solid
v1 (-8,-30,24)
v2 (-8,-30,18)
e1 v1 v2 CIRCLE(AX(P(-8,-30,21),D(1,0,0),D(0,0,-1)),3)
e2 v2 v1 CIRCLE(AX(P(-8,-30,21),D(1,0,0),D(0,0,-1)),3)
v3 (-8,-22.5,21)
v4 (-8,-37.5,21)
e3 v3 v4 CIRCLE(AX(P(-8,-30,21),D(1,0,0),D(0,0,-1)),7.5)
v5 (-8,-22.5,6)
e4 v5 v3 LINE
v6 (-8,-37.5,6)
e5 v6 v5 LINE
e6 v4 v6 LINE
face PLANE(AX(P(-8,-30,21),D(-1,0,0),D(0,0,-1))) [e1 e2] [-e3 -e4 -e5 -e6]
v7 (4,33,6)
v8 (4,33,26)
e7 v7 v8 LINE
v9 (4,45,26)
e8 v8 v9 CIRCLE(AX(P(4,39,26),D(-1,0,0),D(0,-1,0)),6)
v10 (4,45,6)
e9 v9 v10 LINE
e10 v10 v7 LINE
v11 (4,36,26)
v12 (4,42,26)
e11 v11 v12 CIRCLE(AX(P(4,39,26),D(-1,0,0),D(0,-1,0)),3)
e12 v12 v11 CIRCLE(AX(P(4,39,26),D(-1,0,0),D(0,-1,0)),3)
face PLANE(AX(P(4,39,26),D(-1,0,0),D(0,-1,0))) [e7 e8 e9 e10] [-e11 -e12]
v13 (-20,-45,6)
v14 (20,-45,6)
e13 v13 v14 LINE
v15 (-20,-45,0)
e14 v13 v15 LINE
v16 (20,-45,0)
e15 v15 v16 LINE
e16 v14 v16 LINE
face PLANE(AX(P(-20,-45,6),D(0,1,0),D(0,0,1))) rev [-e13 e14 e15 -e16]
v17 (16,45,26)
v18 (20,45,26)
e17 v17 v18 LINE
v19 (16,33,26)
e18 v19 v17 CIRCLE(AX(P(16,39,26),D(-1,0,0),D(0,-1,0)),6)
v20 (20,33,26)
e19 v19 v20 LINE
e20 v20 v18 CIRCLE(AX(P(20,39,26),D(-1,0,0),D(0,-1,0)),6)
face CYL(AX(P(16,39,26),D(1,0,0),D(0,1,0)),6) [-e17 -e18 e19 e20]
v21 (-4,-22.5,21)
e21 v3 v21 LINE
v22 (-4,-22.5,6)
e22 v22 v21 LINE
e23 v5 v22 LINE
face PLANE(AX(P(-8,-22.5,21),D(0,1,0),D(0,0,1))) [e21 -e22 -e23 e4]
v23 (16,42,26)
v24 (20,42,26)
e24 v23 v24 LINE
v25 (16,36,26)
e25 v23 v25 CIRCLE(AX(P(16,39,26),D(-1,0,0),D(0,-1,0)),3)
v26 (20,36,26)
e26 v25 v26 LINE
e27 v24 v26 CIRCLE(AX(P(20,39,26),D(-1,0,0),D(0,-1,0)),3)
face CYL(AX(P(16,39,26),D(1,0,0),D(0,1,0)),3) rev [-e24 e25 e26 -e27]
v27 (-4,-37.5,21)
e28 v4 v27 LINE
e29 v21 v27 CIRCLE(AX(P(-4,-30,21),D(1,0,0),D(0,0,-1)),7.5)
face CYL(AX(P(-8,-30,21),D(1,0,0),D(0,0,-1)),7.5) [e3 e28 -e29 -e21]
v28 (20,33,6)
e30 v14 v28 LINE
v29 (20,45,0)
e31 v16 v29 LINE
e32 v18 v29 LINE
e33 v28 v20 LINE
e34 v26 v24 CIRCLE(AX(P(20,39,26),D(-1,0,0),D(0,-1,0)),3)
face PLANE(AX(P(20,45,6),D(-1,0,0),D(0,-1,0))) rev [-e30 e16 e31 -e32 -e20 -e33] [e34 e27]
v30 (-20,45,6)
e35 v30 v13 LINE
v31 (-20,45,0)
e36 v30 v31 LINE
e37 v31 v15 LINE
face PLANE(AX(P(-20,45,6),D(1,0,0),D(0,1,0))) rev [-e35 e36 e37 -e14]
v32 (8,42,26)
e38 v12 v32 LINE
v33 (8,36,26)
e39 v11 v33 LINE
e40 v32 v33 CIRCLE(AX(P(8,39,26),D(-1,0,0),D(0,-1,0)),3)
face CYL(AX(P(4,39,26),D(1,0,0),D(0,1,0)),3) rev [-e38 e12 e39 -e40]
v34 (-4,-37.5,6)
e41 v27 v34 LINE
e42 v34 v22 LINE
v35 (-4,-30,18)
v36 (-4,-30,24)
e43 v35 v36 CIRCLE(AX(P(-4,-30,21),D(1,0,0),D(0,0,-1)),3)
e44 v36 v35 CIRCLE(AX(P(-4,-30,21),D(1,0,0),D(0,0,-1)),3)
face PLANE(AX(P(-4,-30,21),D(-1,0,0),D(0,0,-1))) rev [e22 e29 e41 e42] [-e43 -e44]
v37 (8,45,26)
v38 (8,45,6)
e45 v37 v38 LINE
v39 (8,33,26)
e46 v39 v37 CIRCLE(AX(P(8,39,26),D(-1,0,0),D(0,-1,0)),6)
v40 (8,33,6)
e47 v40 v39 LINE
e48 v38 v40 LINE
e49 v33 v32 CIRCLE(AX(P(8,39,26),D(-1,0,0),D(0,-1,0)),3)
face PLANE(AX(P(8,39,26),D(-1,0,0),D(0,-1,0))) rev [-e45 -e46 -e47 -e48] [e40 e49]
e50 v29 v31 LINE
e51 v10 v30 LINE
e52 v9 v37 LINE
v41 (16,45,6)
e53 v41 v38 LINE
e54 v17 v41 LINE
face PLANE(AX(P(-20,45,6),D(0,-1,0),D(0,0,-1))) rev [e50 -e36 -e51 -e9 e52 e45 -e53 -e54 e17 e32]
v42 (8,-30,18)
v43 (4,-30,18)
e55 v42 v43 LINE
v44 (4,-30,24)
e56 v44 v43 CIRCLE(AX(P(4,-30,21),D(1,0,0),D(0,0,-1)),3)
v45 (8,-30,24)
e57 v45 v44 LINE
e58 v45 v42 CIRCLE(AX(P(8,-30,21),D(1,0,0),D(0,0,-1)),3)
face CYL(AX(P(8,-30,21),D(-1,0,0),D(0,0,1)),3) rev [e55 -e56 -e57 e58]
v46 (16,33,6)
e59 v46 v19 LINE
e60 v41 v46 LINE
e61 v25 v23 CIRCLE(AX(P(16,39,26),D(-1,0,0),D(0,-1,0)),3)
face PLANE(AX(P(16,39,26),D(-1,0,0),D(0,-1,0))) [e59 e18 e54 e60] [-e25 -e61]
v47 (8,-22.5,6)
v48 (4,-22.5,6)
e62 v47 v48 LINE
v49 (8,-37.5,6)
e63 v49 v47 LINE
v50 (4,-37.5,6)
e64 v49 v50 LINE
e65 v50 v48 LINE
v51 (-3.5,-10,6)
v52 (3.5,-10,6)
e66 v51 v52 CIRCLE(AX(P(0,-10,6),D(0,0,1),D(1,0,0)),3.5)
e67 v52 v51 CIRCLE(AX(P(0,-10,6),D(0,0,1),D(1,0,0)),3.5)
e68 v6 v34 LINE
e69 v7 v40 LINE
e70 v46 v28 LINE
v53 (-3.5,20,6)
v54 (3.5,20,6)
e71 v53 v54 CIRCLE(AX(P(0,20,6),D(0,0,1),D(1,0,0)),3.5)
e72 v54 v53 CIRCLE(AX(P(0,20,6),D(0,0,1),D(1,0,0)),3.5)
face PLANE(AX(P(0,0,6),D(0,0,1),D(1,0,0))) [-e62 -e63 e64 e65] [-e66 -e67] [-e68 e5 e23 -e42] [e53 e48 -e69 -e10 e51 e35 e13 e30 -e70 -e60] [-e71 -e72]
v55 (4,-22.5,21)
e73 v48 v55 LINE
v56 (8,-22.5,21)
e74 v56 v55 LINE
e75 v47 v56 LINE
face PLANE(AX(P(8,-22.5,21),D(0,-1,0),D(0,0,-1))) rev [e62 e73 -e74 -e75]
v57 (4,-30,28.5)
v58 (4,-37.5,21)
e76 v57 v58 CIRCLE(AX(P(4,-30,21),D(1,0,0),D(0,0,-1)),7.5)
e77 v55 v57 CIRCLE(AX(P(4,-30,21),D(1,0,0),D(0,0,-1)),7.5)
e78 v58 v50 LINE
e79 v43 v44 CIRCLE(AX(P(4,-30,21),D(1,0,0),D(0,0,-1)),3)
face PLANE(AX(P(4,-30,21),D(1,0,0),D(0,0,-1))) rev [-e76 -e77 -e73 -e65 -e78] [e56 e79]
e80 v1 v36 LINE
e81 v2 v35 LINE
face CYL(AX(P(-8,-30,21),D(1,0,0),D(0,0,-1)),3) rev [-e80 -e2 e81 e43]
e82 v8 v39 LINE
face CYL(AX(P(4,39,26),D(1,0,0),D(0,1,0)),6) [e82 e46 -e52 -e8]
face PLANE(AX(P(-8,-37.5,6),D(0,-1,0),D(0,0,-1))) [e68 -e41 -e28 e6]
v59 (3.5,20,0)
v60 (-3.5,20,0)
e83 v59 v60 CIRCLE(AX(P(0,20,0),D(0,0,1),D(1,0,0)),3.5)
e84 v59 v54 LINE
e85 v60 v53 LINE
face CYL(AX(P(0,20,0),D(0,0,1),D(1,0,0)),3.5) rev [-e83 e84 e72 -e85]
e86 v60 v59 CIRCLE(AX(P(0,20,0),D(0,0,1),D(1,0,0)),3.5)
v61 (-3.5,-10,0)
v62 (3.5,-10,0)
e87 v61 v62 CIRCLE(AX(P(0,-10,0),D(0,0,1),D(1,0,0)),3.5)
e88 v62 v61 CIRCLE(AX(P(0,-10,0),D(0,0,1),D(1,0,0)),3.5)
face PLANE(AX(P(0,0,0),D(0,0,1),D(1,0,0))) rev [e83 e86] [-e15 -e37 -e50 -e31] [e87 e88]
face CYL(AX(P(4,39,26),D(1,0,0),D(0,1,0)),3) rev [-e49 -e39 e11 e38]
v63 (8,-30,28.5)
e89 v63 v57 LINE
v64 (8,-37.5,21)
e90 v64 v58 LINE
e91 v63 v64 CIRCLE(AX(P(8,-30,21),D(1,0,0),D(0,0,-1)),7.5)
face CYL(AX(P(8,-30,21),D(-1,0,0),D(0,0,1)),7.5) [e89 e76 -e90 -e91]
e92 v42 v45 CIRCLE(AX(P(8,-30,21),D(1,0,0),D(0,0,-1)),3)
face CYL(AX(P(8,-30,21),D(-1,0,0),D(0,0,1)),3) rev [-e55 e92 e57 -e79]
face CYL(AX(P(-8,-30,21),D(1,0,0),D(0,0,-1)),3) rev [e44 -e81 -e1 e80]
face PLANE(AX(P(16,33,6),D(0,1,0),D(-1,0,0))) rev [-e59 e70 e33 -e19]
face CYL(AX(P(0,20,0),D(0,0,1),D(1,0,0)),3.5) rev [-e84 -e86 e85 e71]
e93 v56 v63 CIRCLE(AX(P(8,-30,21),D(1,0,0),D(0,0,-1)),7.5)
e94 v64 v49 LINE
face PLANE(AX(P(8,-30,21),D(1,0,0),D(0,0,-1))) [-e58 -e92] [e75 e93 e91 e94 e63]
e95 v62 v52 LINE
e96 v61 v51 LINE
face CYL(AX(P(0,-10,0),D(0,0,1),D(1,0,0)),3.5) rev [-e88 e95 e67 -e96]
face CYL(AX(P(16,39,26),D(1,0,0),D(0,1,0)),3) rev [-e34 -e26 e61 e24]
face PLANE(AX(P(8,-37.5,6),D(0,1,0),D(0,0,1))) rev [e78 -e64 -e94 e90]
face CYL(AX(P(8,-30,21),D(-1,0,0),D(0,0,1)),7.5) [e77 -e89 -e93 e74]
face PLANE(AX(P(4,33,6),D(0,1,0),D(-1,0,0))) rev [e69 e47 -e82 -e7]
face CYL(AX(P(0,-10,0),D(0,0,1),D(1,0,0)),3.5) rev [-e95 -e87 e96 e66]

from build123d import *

# Parameters (mm, degrees)
SKETCH1_W           = 40
SKETCH1_H           = 90
BOSS_EXTRUDE1_DEPTH = 6
SKETCH3_R           = 3
BOSS_EXTRUDE2_DEPTH = 4
BOSS_EXTRUDE3_START = 4
SKETCH4_R           = 3
BOSS_EXTRUDE3_DEPTH = 4
LPATTERN1_COUNT     = 2
LPATTERN1_PITCH     = 12
SKETCH5_R           = 3.5
CUT_EXTRUDE1_DEPTH  = 56.686623169


with BuildPart() as part:
    # Sketch1 → Boss-Extrude1 (new body)
    with BuildSketch(Plane.XY):
        Rectangle(SKETCH1_W, SKETCH1_H)
    extrude(amount=BOSS_EXTRUDE1_DEPTH)

    # Sketch3 → Boss-Extrude2 (add)
    with BuildSketch(Plane.ZY.offset(-20)):
        with BuildLine():
            Line((26, 45), (6, 45))
            Line((6, 45), (6, 33))
            Line((6, 33), (26, 33))
            ThreePointArc((26, 33), (32, 39), (26, 45))
        make_face()
        with Locations(Location((26, 39, 0), (0, 0, 270))):
            Circle(SKETCH3_R, mode=Mode.SUBTRACT)
    boss_extrude2 = extrude(amount=BOSS_EXTRUDE2_DEPTH)

    # Sketch4 → Boss-Extrude3 (add)
    with BuildSketch(Plane(origin=(0, 0, 0), x_dir=(0, 0, -1), z_dir=(1, 0, 0)).offset(BOSS_EXTRUDE3_START)):
        with BuildLine():
            Line((-21, -22.5), (-6, -22.5))
            Line((-6, -22.5), (-6, -37.5))
            Line((-6, -37.5), (-21, -37.5))
            ThreePointArc((-21, -37.5), (-28.5, -30), (-21, -22.5))
        make_face()
        with Locations((-21, -30)):
            Circle(SKETCH4_R, mode=Mode.SUBTRACT)
    boss_extrude3 = extrude(amount=BOSS_EXTRUDE3_DEPTH)

    # Mirror1: Boss-Extrude3 across plane
    add(boss_extrude3.mirror(Plane(origin=(0, 0, 0), x_dir=(0, 0, 1), z_dir=(1, 0, 0))))

    # LPattern1: Boss-Extrude2 ×2
    with Locations(*[(-i * LPATTERN1_PITCH, 0, 0) for i in range(1, LPATTERN1_COUNT)]):
        add(boss_extrude2)

    # Sketch5 → Cut-Extrude1 (cut, through all)
    with BuildSketch(Plane.XY.offset(6)):
        with Locations((0, 20)):
            Circle(SKETCH5_R)
        with Locations((0, -10)):
            Circle(SKETCH5_R)
    extrude(amount=-CUT_EXTRUDE1_DEPTH, mode=Mode.SUBTRACT)


solid = part.part
